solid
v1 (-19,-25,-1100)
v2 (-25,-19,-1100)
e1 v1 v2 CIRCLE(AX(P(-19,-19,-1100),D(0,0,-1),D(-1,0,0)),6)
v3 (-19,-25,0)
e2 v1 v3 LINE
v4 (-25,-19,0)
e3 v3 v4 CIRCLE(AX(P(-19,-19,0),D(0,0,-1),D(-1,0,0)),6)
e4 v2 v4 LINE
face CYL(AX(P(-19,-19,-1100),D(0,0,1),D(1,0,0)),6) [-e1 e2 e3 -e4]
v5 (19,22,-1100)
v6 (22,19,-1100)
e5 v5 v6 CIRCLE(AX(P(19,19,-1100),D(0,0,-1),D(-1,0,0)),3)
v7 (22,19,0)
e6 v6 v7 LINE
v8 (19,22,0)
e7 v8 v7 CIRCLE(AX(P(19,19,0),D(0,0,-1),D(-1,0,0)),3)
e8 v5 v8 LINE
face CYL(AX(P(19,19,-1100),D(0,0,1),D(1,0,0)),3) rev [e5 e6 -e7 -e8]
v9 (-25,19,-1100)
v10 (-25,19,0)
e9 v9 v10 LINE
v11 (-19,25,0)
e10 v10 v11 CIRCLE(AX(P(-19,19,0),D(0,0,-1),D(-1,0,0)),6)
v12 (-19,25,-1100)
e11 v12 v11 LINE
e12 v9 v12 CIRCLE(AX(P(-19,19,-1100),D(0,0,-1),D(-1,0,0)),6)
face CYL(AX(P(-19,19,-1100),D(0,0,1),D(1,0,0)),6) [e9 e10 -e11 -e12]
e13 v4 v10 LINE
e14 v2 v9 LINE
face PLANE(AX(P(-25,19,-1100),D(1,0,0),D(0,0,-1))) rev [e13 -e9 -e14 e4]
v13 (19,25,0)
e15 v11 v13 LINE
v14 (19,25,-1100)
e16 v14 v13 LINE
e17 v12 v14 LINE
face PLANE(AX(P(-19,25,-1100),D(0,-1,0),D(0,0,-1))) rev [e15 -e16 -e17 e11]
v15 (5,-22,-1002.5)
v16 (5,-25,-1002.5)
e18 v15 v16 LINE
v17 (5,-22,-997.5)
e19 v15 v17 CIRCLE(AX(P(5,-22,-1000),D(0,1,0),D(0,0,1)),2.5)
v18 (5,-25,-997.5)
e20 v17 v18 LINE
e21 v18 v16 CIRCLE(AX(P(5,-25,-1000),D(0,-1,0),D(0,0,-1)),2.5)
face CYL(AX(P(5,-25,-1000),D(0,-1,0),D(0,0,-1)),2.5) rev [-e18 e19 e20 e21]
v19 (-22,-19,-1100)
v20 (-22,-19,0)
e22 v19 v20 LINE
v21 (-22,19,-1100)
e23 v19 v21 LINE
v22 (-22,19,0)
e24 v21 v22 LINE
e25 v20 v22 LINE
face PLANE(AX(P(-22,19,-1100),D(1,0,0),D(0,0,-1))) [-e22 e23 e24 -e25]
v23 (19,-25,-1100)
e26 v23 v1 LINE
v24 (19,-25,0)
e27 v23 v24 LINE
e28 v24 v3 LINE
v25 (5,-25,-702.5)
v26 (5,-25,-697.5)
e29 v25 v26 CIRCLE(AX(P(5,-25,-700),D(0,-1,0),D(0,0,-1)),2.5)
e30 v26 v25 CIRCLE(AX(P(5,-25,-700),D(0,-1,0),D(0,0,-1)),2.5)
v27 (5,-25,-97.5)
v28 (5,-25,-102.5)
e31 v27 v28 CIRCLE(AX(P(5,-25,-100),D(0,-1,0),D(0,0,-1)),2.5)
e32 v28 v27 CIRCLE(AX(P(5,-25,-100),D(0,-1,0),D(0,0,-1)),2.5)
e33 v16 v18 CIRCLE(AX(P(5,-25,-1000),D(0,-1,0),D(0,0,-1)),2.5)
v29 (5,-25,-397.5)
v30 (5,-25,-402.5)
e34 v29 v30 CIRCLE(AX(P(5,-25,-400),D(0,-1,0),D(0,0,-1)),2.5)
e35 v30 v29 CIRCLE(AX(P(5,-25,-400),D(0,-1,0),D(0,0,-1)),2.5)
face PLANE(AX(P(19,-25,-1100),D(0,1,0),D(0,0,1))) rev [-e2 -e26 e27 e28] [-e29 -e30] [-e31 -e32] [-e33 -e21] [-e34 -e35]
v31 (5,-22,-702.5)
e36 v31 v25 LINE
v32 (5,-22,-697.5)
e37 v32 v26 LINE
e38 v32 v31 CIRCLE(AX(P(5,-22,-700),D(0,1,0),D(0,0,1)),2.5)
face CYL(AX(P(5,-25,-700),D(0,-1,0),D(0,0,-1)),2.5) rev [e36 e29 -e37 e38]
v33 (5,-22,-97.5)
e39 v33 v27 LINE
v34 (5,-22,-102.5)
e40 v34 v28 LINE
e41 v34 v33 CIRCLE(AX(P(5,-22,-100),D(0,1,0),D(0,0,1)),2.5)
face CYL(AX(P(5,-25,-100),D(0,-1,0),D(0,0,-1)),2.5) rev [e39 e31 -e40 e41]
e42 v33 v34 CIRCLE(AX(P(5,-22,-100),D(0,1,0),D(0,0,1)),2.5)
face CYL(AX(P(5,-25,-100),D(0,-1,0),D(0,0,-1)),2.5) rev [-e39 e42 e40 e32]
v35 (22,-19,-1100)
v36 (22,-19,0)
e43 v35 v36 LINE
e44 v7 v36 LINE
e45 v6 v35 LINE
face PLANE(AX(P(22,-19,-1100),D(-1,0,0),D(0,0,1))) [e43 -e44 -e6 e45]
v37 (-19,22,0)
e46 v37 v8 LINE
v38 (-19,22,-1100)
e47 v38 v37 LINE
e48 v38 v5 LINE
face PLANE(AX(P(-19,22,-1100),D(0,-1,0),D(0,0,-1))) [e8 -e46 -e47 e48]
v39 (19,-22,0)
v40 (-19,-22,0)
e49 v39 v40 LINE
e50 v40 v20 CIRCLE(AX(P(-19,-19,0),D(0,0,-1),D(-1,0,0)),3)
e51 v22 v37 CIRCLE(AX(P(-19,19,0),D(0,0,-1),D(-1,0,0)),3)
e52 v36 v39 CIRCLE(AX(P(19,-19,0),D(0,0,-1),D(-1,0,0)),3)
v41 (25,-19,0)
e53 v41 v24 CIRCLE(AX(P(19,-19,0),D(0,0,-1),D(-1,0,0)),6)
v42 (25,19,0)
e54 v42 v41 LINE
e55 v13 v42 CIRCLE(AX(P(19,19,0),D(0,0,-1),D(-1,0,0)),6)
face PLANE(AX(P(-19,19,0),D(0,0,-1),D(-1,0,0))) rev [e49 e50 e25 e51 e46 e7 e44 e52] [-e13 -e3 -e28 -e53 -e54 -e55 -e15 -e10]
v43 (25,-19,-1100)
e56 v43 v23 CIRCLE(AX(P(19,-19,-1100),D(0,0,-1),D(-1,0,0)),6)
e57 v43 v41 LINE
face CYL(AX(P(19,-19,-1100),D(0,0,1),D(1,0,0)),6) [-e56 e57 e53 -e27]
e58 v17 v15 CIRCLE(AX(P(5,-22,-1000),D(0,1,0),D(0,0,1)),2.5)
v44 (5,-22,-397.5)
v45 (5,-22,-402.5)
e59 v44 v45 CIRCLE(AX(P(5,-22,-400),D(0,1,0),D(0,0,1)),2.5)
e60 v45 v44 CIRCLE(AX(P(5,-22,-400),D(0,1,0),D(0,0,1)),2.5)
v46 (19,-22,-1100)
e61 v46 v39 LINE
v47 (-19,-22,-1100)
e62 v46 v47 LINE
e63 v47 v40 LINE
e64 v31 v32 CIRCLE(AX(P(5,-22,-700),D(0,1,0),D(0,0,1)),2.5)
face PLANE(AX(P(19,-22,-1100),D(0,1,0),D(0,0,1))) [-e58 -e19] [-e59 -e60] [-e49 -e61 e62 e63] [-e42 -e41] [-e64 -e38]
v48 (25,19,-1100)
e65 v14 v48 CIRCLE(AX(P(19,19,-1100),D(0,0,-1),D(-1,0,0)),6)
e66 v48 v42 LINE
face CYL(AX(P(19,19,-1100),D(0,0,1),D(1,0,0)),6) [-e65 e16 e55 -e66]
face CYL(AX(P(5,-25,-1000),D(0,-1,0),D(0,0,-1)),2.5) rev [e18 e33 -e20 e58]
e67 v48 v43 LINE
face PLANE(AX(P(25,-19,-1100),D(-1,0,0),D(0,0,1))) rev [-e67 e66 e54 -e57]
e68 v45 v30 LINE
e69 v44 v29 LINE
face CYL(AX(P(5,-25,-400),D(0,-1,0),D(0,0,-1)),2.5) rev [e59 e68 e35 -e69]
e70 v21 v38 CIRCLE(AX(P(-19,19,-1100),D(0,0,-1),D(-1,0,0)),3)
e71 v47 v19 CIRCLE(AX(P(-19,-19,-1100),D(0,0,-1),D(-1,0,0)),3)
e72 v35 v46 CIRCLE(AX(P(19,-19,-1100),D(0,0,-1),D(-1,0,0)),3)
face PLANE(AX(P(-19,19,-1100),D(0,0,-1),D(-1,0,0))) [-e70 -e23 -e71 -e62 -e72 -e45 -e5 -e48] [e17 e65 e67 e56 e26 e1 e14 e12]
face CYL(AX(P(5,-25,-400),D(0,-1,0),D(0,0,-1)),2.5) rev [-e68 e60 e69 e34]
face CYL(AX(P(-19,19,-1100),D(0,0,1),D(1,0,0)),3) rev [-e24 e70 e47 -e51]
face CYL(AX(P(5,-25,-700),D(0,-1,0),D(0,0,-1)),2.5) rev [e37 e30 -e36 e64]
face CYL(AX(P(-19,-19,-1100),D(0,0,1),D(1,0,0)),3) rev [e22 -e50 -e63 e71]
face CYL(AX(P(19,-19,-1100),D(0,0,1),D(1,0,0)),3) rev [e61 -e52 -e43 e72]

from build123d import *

# Parameters (mm, degrees)
GB_6728_1986_050_X_50_X_3_1_DEPTH = 1100
HOLE_WIZARD_M6_1_D                = 5
HOLE_WIZARD_M6_1_DEPTH            = 15
HOLE_WIZARD_M6_1_TIP              = 1.502151548


with BuildPart() as part:
    # Sketch1 → Gb／6728-1986方形空心型钢 050 X 50 X 3(1) (new body)
    with BuildSketch(Plane(origin=(0, 0, 0), x_dir=(-1, 0, 0), z_dir=(0, 0, -1))):
        with BuildLine():
            Line((-19, -25), (19, -25))
            ThreePointArc((19, -25), (23.242640687, -23.242640687), (25, -19))
            Line((25, -19), (25, 19))
            ThreePointArc((25, 19), (23.242640687, 23.242640687), (19, 25))
            Line((19, 25), (-19, 25))
            ThreePointArc((-19, 25), (-23.242640687, 23.242640687), (-25, 19))
            Line((-25, 19), (-25, -19))
            ThreePointArc((-25, -19), (-23.242640687, -23.242640687), (-19, -25))
        make_face()
        with BuildLine():
            Line((-19, -22), (19, -22))
            ThreePointArc((19, -22), (21.121320344, -21.121320344), (22, -19))
            Line((22, -19), (22, 19))
            ThreePointArc((22, 19), (21.121320344, 21.121320344), (19, 22))
            Line((19, 22), (-19, 22))
            ThreePointArc((-19, 22), (-21.121320344, 21.121320344), (-22, 19))
            Line((-22, 19), (-22, -19))
            ThreePointArc((-22, -19), (-21.121320344, -21.121320344), (-19, -22))
        make_face(mode=Mode.SUBTRACT)
    extrude(amount=GB_6728_1986_050_X_50_X_3_1_DEPTH)

    # M6 螺纹孔1
    with Locations(Plane(origin=(0, -25, 0), x_dir=(-1, 0, 0), z_dir=(0, -1, 0))):
        with Locations((-5, 100), (-5, 400), (-5, 700), (-5, 1000)):
            Hole(HOLE_WIZARD_M6_1_D / 2, depth=HOLE_WIZARD_M6_1_DEPTH)
            with Locations((0, 0, -(HOLE_WIZARD_M6_1_DEPTH + HOLE_WIZARD_M6_1_TIP / 2))):  # 118° drill point
                Cone(0, HOLE_WIZARD_M6_1_D / 2, HOLE_WIZARD_M6_1_TIP, mode=Mode.SUBTRACT)


solid = part.part
